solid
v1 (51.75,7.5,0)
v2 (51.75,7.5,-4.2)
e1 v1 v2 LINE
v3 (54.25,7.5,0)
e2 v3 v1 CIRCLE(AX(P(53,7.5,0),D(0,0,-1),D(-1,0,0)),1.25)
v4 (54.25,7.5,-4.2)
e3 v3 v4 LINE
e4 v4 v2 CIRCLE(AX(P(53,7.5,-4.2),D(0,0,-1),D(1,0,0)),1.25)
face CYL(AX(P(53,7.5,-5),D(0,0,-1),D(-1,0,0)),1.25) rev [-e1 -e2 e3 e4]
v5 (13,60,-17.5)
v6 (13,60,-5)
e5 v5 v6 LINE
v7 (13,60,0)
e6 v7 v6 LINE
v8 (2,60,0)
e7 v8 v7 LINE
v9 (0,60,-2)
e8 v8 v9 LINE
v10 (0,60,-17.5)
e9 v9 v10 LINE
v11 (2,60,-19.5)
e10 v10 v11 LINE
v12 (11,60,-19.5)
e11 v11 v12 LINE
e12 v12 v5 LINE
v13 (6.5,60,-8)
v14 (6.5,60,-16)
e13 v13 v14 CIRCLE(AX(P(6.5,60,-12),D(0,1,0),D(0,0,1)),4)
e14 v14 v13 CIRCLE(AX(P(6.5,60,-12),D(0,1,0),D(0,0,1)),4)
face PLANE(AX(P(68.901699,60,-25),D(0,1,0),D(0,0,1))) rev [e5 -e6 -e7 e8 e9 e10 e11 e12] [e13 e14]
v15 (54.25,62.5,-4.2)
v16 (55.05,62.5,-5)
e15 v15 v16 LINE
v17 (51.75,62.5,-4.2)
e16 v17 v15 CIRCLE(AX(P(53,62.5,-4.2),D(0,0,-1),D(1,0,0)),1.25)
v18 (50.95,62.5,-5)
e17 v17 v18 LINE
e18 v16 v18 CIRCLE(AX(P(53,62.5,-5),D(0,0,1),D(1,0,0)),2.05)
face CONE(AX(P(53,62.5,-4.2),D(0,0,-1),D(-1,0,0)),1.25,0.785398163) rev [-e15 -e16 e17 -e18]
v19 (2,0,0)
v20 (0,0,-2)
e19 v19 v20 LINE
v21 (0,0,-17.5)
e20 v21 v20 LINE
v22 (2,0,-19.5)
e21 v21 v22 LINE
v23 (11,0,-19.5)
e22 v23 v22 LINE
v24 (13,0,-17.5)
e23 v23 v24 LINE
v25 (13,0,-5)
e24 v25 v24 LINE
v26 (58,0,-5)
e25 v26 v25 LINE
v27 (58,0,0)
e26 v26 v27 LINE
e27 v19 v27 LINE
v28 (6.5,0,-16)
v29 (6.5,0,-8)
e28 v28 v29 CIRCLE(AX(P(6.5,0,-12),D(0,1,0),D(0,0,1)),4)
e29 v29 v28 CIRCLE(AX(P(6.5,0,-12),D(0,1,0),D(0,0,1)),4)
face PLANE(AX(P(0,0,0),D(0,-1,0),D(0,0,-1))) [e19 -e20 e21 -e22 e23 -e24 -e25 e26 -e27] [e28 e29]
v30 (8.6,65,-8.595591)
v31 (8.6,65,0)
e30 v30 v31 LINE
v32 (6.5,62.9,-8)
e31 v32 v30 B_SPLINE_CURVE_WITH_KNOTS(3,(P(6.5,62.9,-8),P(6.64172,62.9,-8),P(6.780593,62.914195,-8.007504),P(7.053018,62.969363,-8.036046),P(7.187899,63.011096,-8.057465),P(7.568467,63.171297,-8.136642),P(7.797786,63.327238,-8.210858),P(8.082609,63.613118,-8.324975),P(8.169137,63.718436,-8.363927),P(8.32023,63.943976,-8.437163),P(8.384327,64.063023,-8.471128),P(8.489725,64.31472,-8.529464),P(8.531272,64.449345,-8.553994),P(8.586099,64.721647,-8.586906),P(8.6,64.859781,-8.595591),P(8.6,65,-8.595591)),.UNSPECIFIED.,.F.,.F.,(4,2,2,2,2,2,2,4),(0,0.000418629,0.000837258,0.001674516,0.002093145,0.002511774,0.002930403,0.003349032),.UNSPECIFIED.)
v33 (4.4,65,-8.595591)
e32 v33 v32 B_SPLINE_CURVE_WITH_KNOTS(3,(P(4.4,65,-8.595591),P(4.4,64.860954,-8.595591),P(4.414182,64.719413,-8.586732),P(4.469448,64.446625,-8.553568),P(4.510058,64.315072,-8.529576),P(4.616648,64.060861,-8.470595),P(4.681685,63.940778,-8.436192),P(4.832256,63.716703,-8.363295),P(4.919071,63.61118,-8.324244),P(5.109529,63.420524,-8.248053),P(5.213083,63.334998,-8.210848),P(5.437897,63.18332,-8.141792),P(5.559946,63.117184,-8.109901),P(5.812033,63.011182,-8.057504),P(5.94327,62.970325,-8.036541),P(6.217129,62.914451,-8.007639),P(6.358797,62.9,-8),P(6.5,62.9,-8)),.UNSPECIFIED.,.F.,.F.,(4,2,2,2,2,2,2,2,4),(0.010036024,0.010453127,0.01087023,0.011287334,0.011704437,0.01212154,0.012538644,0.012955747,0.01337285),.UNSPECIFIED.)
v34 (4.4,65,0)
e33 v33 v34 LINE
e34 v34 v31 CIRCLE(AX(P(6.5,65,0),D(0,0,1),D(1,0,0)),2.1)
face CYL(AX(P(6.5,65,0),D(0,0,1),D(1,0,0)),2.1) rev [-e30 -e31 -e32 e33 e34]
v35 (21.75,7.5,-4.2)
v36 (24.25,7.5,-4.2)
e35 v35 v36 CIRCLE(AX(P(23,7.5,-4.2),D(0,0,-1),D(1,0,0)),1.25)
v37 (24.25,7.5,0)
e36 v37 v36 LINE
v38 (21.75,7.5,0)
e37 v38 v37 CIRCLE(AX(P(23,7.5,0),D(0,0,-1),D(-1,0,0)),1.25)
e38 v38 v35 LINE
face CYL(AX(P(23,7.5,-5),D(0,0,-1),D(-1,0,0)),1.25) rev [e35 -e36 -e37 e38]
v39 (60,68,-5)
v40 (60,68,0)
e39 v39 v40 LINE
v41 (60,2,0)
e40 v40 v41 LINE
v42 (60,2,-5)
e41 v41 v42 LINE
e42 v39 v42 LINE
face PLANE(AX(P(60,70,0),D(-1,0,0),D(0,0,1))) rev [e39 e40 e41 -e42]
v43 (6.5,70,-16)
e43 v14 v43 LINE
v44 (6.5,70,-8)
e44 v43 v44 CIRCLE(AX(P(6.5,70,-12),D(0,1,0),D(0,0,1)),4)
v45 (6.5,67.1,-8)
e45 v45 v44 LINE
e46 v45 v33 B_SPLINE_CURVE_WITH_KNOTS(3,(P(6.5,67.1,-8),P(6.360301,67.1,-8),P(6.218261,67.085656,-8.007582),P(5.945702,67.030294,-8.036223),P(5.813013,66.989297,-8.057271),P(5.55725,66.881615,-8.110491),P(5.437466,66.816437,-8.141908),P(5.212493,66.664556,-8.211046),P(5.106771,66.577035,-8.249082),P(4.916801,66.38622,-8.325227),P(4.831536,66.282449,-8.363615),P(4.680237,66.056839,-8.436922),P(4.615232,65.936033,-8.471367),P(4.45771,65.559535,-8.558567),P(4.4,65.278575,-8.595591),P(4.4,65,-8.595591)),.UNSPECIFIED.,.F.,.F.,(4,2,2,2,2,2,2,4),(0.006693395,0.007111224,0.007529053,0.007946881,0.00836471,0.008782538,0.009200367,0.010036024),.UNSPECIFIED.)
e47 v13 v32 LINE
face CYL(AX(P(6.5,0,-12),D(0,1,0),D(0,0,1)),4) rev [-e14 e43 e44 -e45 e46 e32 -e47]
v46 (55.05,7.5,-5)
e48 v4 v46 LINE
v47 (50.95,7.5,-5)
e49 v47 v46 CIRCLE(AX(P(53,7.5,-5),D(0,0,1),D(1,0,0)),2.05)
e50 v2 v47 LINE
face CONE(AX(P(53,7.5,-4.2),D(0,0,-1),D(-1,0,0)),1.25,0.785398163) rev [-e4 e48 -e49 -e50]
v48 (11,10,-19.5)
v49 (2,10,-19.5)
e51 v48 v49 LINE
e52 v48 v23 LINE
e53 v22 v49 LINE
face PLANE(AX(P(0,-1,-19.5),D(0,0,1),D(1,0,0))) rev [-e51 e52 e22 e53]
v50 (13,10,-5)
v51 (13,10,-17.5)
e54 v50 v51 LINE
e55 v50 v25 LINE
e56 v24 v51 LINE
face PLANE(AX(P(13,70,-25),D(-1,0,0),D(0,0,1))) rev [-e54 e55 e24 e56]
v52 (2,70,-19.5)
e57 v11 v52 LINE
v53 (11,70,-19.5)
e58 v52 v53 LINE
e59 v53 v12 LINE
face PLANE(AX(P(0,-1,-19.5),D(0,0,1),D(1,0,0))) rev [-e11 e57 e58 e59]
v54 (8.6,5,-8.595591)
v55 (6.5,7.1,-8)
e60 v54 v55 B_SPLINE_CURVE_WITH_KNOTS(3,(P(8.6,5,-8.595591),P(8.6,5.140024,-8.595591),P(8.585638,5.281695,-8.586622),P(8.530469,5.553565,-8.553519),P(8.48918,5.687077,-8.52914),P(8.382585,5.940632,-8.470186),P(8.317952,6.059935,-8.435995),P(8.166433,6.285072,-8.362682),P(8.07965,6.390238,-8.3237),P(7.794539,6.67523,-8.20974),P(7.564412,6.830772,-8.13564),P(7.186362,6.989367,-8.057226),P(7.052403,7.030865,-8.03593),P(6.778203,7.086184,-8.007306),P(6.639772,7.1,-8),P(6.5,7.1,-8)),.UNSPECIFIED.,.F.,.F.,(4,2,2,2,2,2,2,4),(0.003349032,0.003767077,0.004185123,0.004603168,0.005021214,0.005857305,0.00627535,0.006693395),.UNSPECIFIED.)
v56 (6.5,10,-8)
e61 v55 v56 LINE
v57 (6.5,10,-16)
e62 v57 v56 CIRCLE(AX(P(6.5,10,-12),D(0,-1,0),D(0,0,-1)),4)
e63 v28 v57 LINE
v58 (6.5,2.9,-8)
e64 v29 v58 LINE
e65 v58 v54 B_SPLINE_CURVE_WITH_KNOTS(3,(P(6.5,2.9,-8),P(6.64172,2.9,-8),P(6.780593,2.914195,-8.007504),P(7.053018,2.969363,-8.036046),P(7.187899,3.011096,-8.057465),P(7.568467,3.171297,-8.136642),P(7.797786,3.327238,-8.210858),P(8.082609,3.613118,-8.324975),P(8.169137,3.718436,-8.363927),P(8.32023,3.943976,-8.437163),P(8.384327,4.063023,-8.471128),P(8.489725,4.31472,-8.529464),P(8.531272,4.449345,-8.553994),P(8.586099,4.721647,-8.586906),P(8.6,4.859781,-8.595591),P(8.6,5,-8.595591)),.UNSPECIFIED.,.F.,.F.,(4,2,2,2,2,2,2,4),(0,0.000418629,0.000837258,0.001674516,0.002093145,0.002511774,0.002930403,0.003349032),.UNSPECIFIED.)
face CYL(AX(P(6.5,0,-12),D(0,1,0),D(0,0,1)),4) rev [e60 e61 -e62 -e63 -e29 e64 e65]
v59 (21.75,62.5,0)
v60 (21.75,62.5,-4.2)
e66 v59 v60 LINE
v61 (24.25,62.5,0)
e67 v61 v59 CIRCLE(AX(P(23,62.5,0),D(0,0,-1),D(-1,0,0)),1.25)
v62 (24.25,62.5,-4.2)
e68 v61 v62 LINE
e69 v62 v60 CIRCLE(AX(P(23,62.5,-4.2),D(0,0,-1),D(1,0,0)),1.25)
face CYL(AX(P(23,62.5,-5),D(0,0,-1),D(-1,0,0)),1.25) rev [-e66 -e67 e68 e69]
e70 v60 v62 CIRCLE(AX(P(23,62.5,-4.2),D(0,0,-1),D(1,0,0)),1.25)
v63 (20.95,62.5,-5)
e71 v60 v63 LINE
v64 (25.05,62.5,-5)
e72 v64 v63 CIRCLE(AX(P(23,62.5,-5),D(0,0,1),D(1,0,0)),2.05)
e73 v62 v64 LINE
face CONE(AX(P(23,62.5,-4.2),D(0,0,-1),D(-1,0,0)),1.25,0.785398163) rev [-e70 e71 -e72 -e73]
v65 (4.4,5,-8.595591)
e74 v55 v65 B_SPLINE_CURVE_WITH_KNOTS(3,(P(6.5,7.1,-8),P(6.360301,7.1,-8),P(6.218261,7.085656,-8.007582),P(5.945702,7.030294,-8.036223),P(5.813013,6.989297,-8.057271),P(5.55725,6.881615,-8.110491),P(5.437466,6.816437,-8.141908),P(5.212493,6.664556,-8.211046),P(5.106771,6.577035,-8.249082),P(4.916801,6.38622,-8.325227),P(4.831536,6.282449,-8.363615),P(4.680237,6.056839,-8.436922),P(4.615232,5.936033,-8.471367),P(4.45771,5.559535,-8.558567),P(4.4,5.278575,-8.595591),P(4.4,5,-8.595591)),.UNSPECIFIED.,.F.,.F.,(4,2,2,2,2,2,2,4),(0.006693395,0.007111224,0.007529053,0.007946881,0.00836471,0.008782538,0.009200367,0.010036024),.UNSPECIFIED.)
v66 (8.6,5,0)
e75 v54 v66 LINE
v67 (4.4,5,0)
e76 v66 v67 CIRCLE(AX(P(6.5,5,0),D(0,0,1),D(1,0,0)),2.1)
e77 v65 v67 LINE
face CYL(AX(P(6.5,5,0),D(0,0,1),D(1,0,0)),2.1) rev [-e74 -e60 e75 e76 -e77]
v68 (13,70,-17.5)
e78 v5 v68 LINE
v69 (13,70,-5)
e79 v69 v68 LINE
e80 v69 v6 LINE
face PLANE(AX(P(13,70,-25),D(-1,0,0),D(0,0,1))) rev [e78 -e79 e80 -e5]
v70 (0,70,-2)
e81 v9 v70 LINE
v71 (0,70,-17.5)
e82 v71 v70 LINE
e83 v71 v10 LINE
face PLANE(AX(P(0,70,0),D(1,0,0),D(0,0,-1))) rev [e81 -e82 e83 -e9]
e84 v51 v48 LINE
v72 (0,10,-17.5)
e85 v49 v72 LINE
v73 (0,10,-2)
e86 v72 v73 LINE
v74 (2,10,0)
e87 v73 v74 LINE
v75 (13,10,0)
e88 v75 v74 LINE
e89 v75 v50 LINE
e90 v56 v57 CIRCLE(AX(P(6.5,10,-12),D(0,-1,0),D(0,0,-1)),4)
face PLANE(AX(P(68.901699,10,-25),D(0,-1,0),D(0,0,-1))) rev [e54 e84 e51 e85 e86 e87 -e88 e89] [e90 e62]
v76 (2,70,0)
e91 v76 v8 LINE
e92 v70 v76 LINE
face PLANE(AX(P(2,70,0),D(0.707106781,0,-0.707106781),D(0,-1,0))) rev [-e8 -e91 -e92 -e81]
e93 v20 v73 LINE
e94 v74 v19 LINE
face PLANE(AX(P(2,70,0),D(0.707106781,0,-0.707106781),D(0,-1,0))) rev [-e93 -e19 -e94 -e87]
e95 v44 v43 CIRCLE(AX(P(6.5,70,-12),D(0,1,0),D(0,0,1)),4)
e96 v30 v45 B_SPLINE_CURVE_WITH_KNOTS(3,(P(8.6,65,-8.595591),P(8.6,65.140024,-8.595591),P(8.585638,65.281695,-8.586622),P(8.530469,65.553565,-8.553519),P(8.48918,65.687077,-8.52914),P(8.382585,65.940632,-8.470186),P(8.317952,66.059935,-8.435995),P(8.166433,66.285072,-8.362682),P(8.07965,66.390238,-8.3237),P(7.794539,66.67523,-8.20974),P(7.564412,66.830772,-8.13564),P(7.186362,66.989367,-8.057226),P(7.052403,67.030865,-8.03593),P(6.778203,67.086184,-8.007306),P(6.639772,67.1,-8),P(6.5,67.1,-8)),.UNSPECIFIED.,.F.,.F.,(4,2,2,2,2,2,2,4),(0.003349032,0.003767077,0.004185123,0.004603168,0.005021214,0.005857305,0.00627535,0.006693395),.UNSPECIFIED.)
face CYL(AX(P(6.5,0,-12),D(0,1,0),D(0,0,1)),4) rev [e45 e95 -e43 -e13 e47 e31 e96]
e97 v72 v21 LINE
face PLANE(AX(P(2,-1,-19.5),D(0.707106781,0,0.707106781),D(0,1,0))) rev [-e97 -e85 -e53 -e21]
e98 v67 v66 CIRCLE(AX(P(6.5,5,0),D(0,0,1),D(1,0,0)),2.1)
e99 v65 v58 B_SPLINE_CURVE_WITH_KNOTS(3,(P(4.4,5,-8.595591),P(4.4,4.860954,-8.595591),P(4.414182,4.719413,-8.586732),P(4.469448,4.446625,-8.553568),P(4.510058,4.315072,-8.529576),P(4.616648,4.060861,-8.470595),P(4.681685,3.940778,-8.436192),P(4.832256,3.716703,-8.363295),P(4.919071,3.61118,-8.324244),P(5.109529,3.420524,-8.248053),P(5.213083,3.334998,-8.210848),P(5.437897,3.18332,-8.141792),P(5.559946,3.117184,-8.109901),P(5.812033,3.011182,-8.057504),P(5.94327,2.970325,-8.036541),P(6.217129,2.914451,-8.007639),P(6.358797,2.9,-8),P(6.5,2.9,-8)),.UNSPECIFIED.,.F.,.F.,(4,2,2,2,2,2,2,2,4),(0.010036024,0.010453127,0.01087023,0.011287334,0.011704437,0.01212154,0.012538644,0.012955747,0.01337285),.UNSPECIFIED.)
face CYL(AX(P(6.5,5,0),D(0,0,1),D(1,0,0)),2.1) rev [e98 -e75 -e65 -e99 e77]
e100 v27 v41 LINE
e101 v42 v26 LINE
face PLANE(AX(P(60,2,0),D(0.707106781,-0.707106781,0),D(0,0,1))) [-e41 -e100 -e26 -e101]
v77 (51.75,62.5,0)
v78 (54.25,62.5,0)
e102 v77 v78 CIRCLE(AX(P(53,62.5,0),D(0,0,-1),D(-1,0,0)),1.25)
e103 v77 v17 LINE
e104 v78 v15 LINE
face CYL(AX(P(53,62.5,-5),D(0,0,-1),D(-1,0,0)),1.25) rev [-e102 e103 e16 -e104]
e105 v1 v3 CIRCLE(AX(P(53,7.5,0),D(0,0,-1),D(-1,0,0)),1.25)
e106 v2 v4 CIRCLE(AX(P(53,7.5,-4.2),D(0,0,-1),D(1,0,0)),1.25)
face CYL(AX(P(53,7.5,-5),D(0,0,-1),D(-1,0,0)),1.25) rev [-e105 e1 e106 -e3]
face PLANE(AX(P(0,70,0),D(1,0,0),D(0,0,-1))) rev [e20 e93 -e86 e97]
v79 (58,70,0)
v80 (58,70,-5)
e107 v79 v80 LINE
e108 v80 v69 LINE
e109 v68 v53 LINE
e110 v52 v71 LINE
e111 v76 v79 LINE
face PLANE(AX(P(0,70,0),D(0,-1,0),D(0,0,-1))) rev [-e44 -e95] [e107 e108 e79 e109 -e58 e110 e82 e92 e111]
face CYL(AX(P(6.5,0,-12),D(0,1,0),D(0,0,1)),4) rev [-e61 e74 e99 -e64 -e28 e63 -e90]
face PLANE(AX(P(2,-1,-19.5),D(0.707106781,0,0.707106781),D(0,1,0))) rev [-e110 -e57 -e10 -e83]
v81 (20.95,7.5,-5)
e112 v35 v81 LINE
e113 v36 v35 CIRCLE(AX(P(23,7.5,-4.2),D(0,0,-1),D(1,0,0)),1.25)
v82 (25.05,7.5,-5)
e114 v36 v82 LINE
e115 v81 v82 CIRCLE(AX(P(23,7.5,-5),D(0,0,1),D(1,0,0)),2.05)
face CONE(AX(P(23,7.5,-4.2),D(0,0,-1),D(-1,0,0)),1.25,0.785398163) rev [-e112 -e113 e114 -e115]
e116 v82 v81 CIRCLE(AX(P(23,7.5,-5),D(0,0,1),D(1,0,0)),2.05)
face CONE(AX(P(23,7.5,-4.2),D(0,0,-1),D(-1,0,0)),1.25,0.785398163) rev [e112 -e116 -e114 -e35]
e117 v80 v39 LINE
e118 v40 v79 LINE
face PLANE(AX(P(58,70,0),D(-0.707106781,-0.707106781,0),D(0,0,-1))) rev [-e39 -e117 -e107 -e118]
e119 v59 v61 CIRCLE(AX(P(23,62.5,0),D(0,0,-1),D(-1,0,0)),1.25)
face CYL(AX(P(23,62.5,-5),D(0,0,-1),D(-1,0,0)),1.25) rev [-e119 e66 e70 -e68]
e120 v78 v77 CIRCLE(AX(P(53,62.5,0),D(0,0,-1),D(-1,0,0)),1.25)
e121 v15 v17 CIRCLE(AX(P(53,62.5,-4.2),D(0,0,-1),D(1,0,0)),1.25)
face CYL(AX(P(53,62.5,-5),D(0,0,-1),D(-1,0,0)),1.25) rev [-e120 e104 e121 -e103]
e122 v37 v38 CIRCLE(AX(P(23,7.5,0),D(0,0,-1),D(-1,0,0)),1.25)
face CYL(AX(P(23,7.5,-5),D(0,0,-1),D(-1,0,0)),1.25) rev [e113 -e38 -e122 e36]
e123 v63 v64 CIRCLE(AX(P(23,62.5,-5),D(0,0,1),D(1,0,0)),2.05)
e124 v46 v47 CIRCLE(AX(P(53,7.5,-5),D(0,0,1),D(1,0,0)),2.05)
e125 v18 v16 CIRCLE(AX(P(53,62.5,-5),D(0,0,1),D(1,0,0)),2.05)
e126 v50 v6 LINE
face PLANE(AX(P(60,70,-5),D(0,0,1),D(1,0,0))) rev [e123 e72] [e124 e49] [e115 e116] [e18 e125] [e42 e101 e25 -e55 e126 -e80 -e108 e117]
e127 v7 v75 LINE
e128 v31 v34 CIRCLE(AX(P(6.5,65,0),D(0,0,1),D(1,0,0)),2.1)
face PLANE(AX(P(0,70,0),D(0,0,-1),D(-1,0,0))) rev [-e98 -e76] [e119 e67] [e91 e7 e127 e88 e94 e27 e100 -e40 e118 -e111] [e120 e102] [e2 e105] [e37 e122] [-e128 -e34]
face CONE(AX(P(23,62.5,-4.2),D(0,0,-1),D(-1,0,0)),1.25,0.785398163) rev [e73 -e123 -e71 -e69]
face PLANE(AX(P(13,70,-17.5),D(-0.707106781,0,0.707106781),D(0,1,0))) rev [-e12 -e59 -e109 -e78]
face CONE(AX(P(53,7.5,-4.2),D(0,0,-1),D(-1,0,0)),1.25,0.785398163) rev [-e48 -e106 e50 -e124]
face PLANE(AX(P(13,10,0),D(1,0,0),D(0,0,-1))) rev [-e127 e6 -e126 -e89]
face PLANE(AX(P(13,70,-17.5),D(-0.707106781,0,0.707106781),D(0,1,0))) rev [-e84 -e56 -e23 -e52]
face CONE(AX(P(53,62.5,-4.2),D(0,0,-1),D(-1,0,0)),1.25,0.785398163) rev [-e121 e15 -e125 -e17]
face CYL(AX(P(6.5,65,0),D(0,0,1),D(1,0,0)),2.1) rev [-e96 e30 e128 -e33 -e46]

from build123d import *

# Parameters (mm, degrees)
BOSS_EXTRUDE1_DEPTH   = 70
SKETCH2_R             = 0.75
CUT_EXTRUDE1_DEPTH    = 10
SKETCH3_W             = 25
SKETCH3_H             = 50
CUT_EXTRUDE2_DEPTH    = 13
SKETCH4_R             = 4
CUT_EXTRUDE3_DEPTH    = 96.524865873
SKETCH5_W             = 13
SKETCH5_H             = 50
BOSS_EXTRUDE2_DEPTH   = 5
SKETCH9_W             = 13
SKETCH9_H             = 5.5
CUT_EXTRUDE6_DEPTH    = 71
LPATTERN1_COUNT       = 2
LPATTERN1_PITCH       = 30
SKETCH10_W            = 13
SKETCH10_H            = 50
CUT_EXTRUDE7_DEPTH    = 95.235078394
CHAMFER1_SIZE         = 2
CHAMFER2_SIZE         = 2
M3_TAPPED_HOLE1_D     = 2.5
M3_TAPPED_HOLE1_DEPTH = 7.5
M3_TAPPED_HOLE1_TIP   = 0.751075774
M5_TAPPED_HOLE1_D     = 4.2
M5_TAPPED_HOLE1_DEPTH = 12.4
M5_TAPPED_HOLE1_TIP   = 1.2618073
M5_TAPPED_HOLE2_D     = 4.2
M5_TAPPED_HOLE2_DEPTH = 12.4
M5_TAPPED_HOLE2_TIP   = 1.2618073
CHAMFER3_SIZE         = 0.8


with BuildPart() as part:
    # Sketch1 → Boss-Extrude1 (new body)
    with BuildSketch(Plane(origin=(0, 0, 0), x_dir=(1, 0, 0), z_dir=(0, 1, 0))):
        Polygon((0, 0), (60, 0), (60, 5), (13, 5), (13, 25), (0, 25), align=None)
    extrude(amount=BOSS_EXTRUDE1_DEPTH)

    # Sketch2 → Cut-Extrude1 (cut)
    with BuildSketch(Plane.XY):
        with Locations((53, 62.5)):
            Circle(SKETCH2_R)
        with Locations((53, 7.5)):
            Circle(SKETCH2_R)
    cut_extrude1 = extrude(amount=-CUT_EXTRUDE1_DEPTH, mode=Mode.SUBTRACT)

    # Sketch3 → Cut-Extrude2 (cut)
    with BuildSketch(Plane.ZY):
        with Locations((-12.5, 35)):
            Rectangle(SKETCH3_W, SKETCH3_H)
    extrude(amount=-CUT_EXTRUDE2_DEPTH, mode=Mode.SUBTRACT)

    # Sketch4 → Cut-Extrude3 (cut, through all)
    with BuildSketch(Plane(origin=(0, 70, 0), x_dir=(1, 0, 0), z_dir=(0, 1, 0))):
        with Locations(Location((6.5, 12, 0), (0, 0, 270))):
            Circle(SKETCH4_R)
    extrude(amount=-CUT_EXTRUDE3_DEPTH, mode=Mode.SUBTRACT)

    # Sketch5 → Boss-Extrude2 (add)
    with BuildSketch(Plane.XY):
        with Locations((6.5, 35)):
            Rectangle(SKETCH5_W, SKETCH5_H)
    extrude(amount=-BOSS_EXTRUDE2_DEPTH)

    # Sketch9 → Cut-Extrude6 (cut)
    with BuildSketch(Plane(origin=(0, 70, 0), x_dir=(1, 0, 0), z_dir=(0, 1, 0))):
        with Locations((6.5, 22.25)):
            Rectangle(SKETCH9_W, SKETCH9_H)
    extrude(amount=-CUT_EXTRUDE6_DEPTH, mode=Mode.SUBTRACT)

    # LPattern1: Cut-Extrude1 ×2
    with Locations(*[(-i * LPATTERN1_PITCH, 0, 0) for i in range(1, LPATTERN1_COUNT)]):
        add(cut_extrude1, mode=Mode.SUBTRACT)

    # Sketch10 → Cut-Extrude7 (cut, through all)
    with BuildSketch(Plane(origin=(0, 0, -19.5), x_dir=(-1, 0, 0), z_dir=(0, 0, -1))):
        with Locations((-6.5, 35)):
            Rectangle(SKETCH10_W, SKETCH10_H)
    extrude(amount=-CUT_EXTRUDE7_DEPTH, mode=Mode.SUBTRACT)

    # Chamfer1
    chamfer1_edges = [part.edges().sort_by_distance(p)[0] for p in [
        (0, 65, 0),
        (0, 5, 0),
        (0, 5, -19.5),
        (0, 65, -19.5),
        (13, 5, -19.5),
        (13, 65, -19.5),
    ]]
    chamfer(chamfer1_edges, length=CHAMFER1_SIZE)

    # Chamfer2
    chamfer2_edges = [part.edges().sort_by_distance(p)[0] for p in [
        (60, 70, -2.5),
        (60, 0, -2.5),
    ]]
    chamfer(chamfer2_edges, length=CHAMFER2_SIZE)

    # M3 Tapped Hole1
    with Locations(Plane(origin=(23, 7.5, -5), x_dir=(-1, 0, 0), z_dir=(0, 0, -1))):
        with Locations((0, 0), (-30, 0), (-30, 55), (0, 55)):
            Hole(M3_TAPPED_HOLE1_D / 2, depth=M3_TAPPED_HOLE1_DEPTH)
            with Locations((0, 0, -(M3_TAPPED_HOLE1_DEPTH + M3_TAPPED_HOLE1_TIP / 2))):  # 118° drill point
                Cone(0, M3_TAPPED_HOLE1_D / 2, M3_TAPPED_HOLE1_TIP, mode=Mode.SUBTRACT)

    # M5 Tapped Hole1
    with Locations(Plane(origin=(6.5, 5, 0), x_dir=(1, 0, 0), z_dir=(0, 0, 1))):
        with Locations((0, 0)):
            Hole(M5_TAPPED_HOLE1_D / 2, depth=M5_TAPPED_HOLE1_DEPTH)
            with Locations((0, 0, -(M5_TAPPED_HOLE1_DEPTH + M5_TAPPED_HOLE1_TIP / 2))):  # 118° drill point
                Cone(0, M5_TAPPED_HOLE1_D / 2, M5_TAPPED_HOLE1_TIP, mode=Mode.SUBTRACT)

    # M5 Tapped Hole2
    with Locations(Plane(origin=(6.5, 65, 0), x_dir=(1, 0, 0), z_dir=(0, 0, 1))):
        with Locations((0, 0)):
            Hole(M5_TAPPED_HOLE2_D / 2, depth=M5_TAPPED_HOLE2_DEPTH)
            with Locations((0, 0, -(M5_TAPPED_HOLE2_DEPTH + M5_TAPPED_HOLE2_TIP / 2))):  # 118° drill point
                Cone(0, M5_TAPPED_HOLE2_D / 2, M5_TAPPED_HOLE2_TIP, mode=Mode.SUBTRACT)

    # Chamfer3
    chamfer3_edges = [part.edges().sort_by_distance(p)[0] for p in [
        (21.75, 62.5, -5),
        (51.75, 62.5, -5),
        (51.75, 7.5, -5),
        (21.75, 7.5, -5),
    ]]
    chamfer(chamfer3_edges, length=CHAMFER3_SIZE)


solid = part.part
